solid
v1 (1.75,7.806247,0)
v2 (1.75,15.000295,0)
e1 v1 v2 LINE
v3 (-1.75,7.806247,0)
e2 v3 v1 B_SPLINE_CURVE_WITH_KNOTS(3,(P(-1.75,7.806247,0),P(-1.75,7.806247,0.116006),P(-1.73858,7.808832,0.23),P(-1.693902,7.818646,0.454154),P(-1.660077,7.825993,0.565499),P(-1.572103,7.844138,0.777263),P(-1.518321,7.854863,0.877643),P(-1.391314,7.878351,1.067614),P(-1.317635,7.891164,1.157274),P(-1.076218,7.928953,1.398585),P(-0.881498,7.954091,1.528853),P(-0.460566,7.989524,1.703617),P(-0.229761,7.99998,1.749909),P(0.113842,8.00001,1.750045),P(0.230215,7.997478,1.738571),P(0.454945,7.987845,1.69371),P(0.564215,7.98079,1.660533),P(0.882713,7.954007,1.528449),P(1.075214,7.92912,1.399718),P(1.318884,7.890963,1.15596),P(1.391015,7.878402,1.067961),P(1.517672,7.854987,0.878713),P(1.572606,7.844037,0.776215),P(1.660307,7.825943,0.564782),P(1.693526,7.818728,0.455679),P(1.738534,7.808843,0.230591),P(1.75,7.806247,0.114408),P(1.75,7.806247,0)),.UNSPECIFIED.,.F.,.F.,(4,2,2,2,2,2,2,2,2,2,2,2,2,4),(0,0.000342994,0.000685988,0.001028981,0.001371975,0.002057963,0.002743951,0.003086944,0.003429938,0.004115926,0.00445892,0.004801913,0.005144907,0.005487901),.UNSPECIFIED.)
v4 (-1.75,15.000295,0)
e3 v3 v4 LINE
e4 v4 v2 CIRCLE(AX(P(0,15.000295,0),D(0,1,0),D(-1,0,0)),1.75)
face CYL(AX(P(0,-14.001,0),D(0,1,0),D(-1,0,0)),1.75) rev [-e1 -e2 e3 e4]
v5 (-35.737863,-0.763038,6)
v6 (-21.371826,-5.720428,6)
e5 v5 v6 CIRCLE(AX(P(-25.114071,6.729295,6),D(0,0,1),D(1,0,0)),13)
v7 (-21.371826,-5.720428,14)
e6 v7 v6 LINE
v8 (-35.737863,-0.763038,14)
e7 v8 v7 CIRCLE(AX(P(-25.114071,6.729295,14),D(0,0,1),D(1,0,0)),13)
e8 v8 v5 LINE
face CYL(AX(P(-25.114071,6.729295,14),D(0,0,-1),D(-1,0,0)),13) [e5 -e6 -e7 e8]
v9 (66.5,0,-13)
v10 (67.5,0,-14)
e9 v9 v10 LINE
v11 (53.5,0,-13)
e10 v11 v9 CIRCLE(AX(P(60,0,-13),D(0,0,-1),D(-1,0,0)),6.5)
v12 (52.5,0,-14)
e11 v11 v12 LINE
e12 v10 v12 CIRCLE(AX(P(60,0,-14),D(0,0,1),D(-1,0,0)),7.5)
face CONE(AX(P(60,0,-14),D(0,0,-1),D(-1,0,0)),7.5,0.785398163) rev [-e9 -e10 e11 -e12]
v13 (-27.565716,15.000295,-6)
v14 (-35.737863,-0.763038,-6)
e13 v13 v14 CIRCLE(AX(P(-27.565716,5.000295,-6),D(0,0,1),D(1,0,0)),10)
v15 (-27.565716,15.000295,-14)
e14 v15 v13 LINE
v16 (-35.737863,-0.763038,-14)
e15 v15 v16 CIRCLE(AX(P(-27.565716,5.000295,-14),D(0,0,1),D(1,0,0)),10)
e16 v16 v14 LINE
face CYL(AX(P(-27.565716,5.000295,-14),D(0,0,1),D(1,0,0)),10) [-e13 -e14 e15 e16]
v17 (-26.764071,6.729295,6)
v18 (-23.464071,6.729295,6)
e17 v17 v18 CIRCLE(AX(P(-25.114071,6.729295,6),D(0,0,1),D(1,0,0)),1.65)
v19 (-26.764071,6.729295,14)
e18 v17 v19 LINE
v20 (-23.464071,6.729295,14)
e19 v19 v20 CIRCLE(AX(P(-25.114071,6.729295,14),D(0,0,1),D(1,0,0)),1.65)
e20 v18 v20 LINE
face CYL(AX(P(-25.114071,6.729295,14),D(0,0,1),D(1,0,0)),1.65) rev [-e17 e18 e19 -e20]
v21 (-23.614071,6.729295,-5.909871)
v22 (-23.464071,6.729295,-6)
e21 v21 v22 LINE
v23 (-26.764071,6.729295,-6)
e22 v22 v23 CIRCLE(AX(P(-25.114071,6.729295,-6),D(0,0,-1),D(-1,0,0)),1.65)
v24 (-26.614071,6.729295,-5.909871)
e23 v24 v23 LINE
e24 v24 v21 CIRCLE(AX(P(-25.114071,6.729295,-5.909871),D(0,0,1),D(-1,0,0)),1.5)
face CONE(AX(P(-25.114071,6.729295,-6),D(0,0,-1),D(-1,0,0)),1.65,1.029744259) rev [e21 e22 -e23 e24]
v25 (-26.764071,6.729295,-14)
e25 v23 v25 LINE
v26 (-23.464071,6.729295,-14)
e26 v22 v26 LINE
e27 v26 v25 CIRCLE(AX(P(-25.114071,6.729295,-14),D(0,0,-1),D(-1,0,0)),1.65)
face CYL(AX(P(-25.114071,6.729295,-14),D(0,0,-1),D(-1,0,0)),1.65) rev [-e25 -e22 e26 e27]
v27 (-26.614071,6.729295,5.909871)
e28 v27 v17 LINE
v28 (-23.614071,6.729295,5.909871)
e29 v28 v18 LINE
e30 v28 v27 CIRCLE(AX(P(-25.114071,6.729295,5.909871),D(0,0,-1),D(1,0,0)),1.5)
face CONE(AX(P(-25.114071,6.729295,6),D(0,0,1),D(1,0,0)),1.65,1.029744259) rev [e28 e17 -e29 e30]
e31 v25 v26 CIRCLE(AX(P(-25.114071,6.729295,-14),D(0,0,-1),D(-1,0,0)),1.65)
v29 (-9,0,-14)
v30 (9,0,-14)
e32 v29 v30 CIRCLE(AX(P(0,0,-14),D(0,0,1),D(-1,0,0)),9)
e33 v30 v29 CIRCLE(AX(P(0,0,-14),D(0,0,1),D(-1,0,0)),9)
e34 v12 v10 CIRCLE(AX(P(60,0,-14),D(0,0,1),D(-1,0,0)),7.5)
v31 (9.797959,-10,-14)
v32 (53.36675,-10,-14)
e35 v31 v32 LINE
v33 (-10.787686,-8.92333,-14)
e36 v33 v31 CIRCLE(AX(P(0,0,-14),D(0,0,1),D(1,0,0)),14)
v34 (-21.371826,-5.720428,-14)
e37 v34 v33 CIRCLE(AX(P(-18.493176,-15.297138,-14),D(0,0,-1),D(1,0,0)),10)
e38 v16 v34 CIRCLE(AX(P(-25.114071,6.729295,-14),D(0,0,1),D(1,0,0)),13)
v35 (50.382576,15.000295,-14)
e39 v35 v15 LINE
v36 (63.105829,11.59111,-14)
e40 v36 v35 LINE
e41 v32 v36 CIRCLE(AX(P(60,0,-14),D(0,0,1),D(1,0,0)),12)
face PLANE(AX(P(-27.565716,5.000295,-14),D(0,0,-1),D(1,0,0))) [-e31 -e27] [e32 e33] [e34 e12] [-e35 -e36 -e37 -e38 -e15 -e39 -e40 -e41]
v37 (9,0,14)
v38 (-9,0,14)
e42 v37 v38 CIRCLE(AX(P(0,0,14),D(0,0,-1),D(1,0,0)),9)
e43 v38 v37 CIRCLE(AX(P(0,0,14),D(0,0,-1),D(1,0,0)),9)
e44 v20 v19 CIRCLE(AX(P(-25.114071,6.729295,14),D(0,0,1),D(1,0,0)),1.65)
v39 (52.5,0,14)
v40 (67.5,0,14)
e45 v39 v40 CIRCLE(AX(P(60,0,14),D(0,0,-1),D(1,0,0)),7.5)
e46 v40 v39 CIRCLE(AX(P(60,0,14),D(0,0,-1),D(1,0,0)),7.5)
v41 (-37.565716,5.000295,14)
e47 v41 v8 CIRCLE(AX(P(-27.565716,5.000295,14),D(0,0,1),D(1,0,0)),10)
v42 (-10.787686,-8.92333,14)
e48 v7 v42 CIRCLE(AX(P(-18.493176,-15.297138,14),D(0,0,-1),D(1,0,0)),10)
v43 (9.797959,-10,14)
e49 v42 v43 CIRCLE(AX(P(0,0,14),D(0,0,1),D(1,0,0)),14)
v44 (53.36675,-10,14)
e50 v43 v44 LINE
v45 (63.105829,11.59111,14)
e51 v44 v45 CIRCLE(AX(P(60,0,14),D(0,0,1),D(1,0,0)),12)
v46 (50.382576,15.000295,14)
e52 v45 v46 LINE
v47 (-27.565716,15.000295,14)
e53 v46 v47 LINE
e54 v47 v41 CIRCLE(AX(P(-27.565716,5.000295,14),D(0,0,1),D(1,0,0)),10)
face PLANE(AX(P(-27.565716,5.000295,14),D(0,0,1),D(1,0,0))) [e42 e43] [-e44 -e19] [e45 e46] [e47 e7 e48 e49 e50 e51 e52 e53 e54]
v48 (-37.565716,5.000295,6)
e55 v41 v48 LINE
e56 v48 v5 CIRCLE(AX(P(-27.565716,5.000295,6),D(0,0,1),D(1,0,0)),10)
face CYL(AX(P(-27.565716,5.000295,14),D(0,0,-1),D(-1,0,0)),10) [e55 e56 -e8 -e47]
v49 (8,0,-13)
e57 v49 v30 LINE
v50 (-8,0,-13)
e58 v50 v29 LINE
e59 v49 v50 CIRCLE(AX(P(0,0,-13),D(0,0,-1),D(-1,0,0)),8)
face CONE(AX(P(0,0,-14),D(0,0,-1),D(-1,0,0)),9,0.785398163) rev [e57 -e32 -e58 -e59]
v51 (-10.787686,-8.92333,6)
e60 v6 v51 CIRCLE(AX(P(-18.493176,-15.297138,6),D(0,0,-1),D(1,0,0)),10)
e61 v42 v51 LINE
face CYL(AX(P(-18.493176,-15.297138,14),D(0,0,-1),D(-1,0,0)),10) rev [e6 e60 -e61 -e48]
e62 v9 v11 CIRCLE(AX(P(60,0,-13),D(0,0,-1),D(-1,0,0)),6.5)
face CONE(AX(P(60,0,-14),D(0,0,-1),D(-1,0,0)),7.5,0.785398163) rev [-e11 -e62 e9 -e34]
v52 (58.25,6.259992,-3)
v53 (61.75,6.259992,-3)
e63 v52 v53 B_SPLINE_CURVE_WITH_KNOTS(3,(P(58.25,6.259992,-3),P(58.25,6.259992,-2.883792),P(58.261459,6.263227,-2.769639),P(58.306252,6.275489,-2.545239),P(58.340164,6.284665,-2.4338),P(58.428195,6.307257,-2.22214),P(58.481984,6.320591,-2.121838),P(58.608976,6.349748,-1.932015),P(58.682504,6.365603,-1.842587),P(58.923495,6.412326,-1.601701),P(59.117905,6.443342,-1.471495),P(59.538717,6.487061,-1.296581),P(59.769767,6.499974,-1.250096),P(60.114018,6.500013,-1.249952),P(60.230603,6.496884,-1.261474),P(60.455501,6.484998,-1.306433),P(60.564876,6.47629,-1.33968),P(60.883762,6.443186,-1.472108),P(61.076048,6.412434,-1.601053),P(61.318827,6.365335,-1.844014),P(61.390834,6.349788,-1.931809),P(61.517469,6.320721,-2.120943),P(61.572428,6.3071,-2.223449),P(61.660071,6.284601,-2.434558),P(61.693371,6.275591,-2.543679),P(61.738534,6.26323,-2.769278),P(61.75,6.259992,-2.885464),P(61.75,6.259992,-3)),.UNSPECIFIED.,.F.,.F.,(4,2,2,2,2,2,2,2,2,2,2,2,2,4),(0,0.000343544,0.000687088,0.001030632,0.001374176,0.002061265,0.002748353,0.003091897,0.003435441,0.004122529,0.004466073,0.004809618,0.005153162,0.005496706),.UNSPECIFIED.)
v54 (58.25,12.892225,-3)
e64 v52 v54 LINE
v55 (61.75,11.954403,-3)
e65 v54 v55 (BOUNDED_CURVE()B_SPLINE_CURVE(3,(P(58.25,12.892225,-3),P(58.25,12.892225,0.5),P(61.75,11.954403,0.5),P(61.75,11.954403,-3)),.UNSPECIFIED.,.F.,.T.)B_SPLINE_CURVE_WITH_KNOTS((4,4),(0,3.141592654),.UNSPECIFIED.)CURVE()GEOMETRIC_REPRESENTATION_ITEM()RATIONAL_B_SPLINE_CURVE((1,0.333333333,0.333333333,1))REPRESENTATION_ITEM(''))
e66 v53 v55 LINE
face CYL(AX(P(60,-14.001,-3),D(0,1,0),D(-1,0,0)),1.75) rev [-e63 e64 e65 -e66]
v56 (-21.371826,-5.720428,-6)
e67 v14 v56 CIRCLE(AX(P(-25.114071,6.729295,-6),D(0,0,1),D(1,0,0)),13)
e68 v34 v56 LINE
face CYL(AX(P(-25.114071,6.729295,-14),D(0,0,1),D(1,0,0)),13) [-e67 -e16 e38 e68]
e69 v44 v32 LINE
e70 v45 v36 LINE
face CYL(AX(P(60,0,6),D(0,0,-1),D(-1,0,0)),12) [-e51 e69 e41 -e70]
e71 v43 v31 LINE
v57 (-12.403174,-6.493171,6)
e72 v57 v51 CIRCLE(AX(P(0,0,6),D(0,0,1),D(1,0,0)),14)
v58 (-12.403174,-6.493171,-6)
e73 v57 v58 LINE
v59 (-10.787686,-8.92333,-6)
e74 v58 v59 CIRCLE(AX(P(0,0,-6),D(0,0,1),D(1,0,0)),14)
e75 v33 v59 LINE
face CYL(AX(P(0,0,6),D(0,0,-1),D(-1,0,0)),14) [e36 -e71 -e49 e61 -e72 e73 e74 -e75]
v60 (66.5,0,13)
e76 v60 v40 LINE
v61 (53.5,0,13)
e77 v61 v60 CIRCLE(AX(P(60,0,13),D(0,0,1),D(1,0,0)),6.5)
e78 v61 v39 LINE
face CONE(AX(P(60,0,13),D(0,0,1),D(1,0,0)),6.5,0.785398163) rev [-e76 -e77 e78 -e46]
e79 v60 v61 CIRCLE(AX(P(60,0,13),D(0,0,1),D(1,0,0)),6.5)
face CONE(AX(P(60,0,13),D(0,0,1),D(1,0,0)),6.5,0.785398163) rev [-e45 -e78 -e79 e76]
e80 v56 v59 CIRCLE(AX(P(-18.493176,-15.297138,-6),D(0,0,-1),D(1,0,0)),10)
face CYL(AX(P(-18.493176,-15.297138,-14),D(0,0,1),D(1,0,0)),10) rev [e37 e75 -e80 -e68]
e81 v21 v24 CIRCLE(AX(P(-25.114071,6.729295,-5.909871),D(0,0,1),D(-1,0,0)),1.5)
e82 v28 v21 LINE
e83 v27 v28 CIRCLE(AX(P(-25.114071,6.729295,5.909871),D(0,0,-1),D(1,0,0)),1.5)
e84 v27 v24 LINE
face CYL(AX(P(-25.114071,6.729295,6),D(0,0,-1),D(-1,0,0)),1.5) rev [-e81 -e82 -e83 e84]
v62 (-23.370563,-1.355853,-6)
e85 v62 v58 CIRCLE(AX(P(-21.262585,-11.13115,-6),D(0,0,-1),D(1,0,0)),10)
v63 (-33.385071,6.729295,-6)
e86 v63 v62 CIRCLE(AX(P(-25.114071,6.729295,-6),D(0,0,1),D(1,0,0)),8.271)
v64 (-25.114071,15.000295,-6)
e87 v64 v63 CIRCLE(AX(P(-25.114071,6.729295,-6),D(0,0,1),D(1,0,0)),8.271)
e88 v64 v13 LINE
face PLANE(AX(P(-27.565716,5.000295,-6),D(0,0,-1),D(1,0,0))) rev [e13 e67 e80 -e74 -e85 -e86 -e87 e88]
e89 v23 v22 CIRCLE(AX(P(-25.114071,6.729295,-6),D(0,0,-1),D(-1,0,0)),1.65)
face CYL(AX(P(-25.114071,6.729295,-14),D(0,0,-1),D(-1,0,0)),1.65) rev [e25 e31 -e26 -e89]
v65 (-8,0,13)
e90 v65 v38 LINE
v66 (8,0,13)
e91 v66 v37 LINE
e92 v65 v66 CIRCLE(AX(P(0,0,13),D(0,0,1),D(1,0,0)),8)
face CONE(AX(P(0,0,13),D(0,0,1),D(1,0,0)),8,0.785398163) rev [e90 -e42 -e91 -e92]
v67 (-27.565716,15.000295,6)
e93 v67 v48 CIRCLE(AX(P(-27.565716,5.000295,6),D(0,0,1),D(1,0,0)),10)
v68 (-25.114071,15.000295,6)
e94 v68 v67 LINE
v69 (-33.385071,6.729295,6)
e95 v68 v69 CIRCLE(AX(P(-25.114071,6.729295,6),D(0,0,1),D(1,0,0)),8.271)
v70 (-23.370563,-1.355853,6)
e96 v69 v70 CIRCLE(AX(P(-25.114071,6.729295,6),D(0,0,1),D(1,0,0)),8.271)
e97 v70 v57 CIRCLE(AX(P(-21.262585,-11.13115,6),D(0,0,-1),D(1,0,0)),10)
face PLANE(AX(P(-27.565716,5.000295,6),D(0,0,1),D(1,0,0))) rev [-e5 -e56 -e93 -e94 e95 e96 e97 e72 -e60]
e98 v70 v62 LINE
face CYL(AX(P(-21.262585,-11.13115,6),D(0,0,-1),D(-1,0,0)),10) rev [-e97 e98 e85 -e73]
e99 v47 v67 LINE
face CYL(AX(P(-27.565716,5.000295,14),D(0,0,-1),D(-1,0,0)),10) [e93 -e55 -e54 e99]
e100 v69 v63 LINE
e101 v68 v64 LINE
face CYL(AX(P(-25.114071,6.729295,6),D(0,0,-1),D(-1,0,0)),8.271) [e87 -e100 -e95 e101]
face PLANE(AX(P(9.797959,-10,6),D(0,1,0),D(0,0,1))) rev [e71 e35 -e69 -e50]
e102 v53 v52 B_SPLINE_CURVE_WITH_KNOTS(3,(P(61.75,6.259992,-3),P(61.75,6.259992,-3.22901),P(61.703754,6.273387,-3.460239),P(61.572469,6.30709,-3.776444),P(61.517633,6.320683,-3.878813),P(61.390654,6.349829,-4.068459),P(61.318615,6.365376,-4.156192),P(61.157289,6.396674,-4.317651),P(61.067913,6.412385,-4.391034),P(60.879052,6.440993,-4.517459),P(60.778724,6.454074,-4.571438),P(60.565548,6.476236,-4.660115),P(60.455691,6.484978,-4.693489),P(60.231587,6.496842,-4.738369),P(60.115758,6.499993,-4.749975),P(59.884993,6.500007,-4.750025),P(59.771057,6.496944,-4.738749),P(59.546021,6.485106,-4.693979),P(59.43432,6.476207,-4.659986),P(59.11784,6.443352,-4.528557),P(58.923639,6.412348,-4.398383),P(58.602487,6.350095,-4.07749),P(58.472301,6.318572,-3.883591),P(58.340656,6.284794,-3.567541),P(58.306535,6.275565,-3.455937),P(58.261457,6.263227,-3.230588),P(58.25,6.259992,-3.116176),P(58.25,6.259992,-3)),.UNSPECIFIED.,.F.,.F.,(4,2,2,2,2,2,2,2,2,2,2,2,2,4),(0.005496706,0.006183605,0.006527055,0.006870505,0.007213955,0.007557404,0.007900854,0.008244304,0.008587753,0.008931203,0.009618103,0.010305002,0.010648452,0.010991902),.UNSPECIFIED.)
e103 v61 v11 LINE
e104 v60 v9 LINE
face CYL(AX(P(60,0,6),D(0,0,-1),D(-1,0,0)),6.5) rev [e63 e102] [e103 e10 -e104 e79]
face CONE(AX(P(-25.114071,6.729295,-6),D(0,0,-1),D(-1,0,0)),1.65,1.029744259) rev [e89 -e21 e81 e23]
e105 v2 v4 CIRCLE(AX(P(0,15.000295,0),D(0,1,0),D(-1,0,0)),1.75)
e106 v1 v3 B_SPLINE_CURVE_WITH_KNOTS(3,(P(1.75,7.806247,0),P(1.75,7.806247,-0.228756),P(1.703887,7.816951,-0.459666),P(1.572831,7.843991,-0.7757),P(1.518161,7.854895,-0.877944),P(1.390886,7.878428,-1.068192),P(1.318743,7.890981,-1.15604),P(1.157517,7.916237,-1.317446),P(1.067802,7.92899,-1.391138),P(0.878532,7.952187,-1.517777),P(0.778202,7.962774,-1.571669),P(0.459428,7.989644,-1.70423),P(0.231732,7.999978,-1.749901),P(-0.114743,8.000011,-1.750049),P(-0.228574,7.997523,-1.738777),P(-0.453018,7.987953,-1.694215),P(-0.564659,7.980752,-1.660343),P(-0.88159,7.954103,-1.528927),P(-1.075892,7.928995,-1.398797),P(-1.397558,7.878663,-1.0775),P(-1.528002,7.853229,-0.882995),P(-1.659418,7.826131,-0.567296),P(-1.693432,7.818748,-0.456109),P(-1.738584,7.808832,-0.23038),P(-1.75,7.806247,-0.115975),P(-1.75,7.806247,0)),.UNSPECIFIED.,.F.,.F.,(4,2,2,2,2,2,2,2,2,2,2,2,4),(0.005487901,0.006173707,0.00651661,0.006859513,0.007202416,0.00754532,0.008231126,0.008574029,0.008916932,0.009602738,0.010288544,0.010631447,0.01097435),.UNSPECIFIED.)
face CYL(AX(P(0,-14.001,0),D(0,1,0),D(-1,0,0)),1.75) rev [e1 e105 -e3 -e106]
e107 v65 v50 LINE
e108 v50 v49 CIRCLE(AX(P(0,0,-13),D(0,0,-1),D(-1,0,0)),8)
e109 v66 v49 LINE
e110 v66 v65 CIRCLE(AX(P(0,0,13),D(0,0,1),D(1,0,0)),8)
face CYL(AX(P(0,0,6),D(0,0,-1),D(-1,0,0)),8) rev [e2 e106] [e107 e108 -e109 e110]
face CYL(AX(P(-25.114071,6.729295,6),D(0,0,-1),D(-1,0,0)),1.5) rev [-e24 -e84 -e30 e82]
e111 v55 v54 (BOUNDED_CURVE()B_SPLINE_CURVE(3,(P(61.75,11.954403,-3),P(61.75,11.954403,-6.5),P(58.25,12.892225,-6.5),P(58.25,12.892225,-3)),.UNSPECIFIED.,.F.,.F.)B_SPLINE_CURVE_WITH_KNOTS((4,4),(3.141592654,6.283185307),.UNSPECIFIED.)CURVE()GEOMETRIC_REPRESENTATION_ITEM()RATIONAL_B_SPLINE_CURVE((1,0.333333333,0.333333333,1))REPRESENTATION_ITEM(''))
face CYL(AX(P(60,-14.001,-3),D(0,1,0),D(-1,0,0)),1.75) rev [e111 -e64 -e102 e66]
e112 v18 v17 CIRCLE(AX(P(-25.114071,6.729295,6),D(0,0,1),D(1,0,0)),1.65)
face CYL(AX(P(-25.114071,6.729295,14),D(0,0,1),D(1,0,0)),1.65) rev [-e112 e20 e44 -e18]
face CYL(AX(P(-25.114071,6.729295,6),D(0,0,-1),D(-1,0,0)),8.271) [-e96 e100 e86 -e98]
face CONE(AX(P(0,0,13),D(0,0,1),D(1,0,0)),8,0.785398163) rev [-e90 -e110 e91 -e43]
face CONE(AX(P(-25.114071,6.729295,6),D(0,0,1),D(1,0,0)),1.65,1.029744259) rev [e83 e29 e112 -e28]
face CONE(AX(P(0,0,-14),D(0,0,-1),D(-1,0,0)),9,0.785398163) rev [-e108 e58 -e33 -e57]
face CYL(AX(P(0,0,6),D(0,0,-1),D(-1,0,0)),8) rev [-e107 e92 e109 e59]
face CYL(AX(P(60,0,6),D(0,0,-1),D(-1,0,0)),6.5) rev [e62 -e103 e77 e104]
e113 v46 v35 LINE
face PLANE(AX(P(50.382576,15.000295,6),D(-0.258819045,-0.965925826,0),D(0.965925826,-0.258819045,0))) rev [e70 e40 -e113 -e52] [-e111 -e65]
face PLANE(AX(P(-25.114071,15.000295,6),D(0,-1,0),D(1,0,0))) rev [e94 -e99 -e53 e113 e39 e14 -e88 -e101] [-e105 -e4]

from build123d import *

# Parameters (mm, degrees)
SKETCH1_R               = 8
SKETCH1_R_2             = 6.5
SKETCH1_R_3             = 1.5
BOSS_EXTRUDE1_DEPTH     = 6
SKETCH2_R               = 6.5
SKETCH2_R_2             = 8
BOSS_EXTRUDE2_DEPTH     = 8
CUT_EXTRUDE1_REACH      = 80.873
CUT_EXTRUDE1_END_RADIUS = 8
SKETCH4_R               = 1.75
CUT_EXTRUDE2_REACH      = 80.873
CUT_EXTRUDE2_END_RADIUS = 6.5
SKETCH5_R               = 1.75
CHAMFER1_SIZE           = 1


with BuildPart() as part:
    # Sketch1 → Boss-Extrude1 (new, symmetric)
    with BuildSketch(Plane.XY):
        with BuildLine():
            Line((9.797958971, -10), (53.366750419, -10))
            ThreePointArc((53.366750419, -10), (70.93867824, -4.934097522), (63.105828541, 11.591109915))
            Line((63.105828541, 11.591109915), (50.382575949, 15.000295173))
            Line((50.382575949, 15.000295173), (-25.114071484, 15.000295173))
            ThreePointArc((-25.114071484, 15.000295173), (-33.338477244, 5.852602019), (-23.370562784, -1.355852842))
            ThreePointArc((-23.370562784, -1.355852842), (-17.0207139, -2.075403858), (-12.40317439, -6.493170646))
            ThreePointArc((-12.40317439, -6.493170646), (-2.184319087, -13.828548374), (9.797958971, -10))
        make_face()
        Circle(SKETCH1_R, mode=Mode.SUBTRACT)
        with Locations((60, 0)):
            Circle(SKETCH1_R_2, mode=Mode.SUBTRACT)
        with Locations((-25.114071484, 6.729295173)):
            Circle(SKETCH1_R_3, mode=Mode.SUBTRACT)
    extrude(amount=BOSS_EXTRUDE1_DEPTH, both=True)

    # Sketch2 → Boss-Extrude2 (add)
    with BuildSketch(Plane.XY.offset(6)):
        with BuildLine():
            Line((50.382575949, 15.000295173), (-27.565715626, 15.000295173))
            ThreePointArc((-27.565715626, 15.000295173), (-36.443590747, 9.602830706), (-35.737862766, -0.763038161))
            ThreePointArc((-35.737862766, -0.763038161), (-29.354690281, -5.559608449), (-21.371826468, -5.720427806))
            ThreePointArc((-21.371826468, -5.720427806), (-15.596757504, -5.725786931), (-10.787686266, -8.923330377))
            ThreePointArc((-10.787686266, -8.923330377), (-0.731228007, -13.98089073), (9.797958971, -10))
            Line((9.797958971, -10), (53.366750419, -10))
            ThreePointArc((53.366750419, -10), (70.93867824, -4.934097522), (63.105828541, 11.591109915))
            Line((63.105828541, 11.591109915), (50.382575949, 15.000295173))
        make_face()
        with Locations((60, 0)):
            Circle(SKETCH2_R, mode=Mode.SUBTRACT)
        Circle(SKETCH2_R_2, mode=Mode.SUBTRACT)
    boss_extrude2 = extrude(amount=BOSS_EXTRUDE2_DEPTH)

    # Mirror1: Boss-Extrude2 across plane
    add(boss_extrude2.mirror(Plane.XY))

    # Sketch3 → M4 Tapped Hole1 (revolve, cut)
    with BuildSketch(Plane(origin=(-25.114071484, 6.729295173, 14), x_dir=(0, -1, 0), z_dir=(1, 0, 0))):
        Polygon((0, 0), (0, 8.991420021), (1.65, 8), (1.65, 0), align=None)
    m4_tapped_hole1 = revolve(axis=Axis((-25.114071484, 6.729295173, 20.35), (0, 0, -1)), mode=Mode.SUBTRACT)

    # Mirror2: M4 Tapped Hole1 across plane
    add(m4_tapped_hole1.mirror(Plane.XY), mode=Mode.SUBTRACT)

    # Cut-Extrude1: up to this cylinder (the profile starts outside it)
    cut_extrude1_end = Plane(origin=(0, 0, 0), z_dir=(0, 0, -1)) * Cylinder(CUT_EXTRUDE1_END_RADIUS, 178.746, mode=Mode.PRIVATE)
    # Sketch4 → Cut-Extrude1 (cut, up to the surface)
    with BuildSketch(Plane(origin=(0, 15.000295173, 0), x_dir=(1, 0, 0), z_dir=(0, 1, 0)), mode=Mode.PRIVATE) as cut_extrude1_sk1:
        with Locations(Location((0, 0, 0), (0, 0, 180))):
            Circle(SKETCH4_R)
    cut_extrude1_tool1 = extrude(cut_extrude1_sk1.sketch, amount=-CUT_EXTRUDE1_REACH, mode=Mode.PRIVATE) - cut_extrude1_end
    add(cut_extrude1_tool1.solids().sort_by_distance((0, 15.000295, 0))[0], mode=Mode.SUBTRACT)

    # Cut-Extrude2: up to this cylinder (the profile starts outside it)
    cut_extrude2_end = Plane(origin=(60, 0, -3), z_dir=(0, 0, -1)) * Cylinder(CUT_EXTRUDE2_END_RADIUS, 175.746, mode=Mode.PRIVATE)
    # Sketch5 → Cut-Extrude2 (cut, up to the surface)
    with BuildSketch(Plane(origin=(0, 15.000295173, 0), x_dir=(1, 0, 0), z_dir=(0, 1, 0)), mode=Mode.PRIVATE) as cut_extrude2_sk1:
        with Locations(Location((60, 3, 0), (0, 0, 180))):
            Circle(SKETCH5_R)
    cut_extrude2_tool1 = extrude(cut_extrude2_sk1.sketch, amount=-CUT_EXTRUDE2_REACH, mode=Mode.PRIVATE) - cut_extrude2_end
    add(cut_extrude2_tool1.solids().sort_by_distance((60, 15.000295, -3))[0], mode=Mode.SUBTRACT)

    # Chamfer1
    chamfer1_edges = [part.edges().sort_by_distance(p)[0] for p in [
        (53.5, 0, 14),
        (-8, 0, 14),
        (-8, 0, -14),
        (53.5, 0, -14),
    ]]
    chamfer(chamfer1_edges, length=CHAMFER1_SIZE)


solid = part.part
